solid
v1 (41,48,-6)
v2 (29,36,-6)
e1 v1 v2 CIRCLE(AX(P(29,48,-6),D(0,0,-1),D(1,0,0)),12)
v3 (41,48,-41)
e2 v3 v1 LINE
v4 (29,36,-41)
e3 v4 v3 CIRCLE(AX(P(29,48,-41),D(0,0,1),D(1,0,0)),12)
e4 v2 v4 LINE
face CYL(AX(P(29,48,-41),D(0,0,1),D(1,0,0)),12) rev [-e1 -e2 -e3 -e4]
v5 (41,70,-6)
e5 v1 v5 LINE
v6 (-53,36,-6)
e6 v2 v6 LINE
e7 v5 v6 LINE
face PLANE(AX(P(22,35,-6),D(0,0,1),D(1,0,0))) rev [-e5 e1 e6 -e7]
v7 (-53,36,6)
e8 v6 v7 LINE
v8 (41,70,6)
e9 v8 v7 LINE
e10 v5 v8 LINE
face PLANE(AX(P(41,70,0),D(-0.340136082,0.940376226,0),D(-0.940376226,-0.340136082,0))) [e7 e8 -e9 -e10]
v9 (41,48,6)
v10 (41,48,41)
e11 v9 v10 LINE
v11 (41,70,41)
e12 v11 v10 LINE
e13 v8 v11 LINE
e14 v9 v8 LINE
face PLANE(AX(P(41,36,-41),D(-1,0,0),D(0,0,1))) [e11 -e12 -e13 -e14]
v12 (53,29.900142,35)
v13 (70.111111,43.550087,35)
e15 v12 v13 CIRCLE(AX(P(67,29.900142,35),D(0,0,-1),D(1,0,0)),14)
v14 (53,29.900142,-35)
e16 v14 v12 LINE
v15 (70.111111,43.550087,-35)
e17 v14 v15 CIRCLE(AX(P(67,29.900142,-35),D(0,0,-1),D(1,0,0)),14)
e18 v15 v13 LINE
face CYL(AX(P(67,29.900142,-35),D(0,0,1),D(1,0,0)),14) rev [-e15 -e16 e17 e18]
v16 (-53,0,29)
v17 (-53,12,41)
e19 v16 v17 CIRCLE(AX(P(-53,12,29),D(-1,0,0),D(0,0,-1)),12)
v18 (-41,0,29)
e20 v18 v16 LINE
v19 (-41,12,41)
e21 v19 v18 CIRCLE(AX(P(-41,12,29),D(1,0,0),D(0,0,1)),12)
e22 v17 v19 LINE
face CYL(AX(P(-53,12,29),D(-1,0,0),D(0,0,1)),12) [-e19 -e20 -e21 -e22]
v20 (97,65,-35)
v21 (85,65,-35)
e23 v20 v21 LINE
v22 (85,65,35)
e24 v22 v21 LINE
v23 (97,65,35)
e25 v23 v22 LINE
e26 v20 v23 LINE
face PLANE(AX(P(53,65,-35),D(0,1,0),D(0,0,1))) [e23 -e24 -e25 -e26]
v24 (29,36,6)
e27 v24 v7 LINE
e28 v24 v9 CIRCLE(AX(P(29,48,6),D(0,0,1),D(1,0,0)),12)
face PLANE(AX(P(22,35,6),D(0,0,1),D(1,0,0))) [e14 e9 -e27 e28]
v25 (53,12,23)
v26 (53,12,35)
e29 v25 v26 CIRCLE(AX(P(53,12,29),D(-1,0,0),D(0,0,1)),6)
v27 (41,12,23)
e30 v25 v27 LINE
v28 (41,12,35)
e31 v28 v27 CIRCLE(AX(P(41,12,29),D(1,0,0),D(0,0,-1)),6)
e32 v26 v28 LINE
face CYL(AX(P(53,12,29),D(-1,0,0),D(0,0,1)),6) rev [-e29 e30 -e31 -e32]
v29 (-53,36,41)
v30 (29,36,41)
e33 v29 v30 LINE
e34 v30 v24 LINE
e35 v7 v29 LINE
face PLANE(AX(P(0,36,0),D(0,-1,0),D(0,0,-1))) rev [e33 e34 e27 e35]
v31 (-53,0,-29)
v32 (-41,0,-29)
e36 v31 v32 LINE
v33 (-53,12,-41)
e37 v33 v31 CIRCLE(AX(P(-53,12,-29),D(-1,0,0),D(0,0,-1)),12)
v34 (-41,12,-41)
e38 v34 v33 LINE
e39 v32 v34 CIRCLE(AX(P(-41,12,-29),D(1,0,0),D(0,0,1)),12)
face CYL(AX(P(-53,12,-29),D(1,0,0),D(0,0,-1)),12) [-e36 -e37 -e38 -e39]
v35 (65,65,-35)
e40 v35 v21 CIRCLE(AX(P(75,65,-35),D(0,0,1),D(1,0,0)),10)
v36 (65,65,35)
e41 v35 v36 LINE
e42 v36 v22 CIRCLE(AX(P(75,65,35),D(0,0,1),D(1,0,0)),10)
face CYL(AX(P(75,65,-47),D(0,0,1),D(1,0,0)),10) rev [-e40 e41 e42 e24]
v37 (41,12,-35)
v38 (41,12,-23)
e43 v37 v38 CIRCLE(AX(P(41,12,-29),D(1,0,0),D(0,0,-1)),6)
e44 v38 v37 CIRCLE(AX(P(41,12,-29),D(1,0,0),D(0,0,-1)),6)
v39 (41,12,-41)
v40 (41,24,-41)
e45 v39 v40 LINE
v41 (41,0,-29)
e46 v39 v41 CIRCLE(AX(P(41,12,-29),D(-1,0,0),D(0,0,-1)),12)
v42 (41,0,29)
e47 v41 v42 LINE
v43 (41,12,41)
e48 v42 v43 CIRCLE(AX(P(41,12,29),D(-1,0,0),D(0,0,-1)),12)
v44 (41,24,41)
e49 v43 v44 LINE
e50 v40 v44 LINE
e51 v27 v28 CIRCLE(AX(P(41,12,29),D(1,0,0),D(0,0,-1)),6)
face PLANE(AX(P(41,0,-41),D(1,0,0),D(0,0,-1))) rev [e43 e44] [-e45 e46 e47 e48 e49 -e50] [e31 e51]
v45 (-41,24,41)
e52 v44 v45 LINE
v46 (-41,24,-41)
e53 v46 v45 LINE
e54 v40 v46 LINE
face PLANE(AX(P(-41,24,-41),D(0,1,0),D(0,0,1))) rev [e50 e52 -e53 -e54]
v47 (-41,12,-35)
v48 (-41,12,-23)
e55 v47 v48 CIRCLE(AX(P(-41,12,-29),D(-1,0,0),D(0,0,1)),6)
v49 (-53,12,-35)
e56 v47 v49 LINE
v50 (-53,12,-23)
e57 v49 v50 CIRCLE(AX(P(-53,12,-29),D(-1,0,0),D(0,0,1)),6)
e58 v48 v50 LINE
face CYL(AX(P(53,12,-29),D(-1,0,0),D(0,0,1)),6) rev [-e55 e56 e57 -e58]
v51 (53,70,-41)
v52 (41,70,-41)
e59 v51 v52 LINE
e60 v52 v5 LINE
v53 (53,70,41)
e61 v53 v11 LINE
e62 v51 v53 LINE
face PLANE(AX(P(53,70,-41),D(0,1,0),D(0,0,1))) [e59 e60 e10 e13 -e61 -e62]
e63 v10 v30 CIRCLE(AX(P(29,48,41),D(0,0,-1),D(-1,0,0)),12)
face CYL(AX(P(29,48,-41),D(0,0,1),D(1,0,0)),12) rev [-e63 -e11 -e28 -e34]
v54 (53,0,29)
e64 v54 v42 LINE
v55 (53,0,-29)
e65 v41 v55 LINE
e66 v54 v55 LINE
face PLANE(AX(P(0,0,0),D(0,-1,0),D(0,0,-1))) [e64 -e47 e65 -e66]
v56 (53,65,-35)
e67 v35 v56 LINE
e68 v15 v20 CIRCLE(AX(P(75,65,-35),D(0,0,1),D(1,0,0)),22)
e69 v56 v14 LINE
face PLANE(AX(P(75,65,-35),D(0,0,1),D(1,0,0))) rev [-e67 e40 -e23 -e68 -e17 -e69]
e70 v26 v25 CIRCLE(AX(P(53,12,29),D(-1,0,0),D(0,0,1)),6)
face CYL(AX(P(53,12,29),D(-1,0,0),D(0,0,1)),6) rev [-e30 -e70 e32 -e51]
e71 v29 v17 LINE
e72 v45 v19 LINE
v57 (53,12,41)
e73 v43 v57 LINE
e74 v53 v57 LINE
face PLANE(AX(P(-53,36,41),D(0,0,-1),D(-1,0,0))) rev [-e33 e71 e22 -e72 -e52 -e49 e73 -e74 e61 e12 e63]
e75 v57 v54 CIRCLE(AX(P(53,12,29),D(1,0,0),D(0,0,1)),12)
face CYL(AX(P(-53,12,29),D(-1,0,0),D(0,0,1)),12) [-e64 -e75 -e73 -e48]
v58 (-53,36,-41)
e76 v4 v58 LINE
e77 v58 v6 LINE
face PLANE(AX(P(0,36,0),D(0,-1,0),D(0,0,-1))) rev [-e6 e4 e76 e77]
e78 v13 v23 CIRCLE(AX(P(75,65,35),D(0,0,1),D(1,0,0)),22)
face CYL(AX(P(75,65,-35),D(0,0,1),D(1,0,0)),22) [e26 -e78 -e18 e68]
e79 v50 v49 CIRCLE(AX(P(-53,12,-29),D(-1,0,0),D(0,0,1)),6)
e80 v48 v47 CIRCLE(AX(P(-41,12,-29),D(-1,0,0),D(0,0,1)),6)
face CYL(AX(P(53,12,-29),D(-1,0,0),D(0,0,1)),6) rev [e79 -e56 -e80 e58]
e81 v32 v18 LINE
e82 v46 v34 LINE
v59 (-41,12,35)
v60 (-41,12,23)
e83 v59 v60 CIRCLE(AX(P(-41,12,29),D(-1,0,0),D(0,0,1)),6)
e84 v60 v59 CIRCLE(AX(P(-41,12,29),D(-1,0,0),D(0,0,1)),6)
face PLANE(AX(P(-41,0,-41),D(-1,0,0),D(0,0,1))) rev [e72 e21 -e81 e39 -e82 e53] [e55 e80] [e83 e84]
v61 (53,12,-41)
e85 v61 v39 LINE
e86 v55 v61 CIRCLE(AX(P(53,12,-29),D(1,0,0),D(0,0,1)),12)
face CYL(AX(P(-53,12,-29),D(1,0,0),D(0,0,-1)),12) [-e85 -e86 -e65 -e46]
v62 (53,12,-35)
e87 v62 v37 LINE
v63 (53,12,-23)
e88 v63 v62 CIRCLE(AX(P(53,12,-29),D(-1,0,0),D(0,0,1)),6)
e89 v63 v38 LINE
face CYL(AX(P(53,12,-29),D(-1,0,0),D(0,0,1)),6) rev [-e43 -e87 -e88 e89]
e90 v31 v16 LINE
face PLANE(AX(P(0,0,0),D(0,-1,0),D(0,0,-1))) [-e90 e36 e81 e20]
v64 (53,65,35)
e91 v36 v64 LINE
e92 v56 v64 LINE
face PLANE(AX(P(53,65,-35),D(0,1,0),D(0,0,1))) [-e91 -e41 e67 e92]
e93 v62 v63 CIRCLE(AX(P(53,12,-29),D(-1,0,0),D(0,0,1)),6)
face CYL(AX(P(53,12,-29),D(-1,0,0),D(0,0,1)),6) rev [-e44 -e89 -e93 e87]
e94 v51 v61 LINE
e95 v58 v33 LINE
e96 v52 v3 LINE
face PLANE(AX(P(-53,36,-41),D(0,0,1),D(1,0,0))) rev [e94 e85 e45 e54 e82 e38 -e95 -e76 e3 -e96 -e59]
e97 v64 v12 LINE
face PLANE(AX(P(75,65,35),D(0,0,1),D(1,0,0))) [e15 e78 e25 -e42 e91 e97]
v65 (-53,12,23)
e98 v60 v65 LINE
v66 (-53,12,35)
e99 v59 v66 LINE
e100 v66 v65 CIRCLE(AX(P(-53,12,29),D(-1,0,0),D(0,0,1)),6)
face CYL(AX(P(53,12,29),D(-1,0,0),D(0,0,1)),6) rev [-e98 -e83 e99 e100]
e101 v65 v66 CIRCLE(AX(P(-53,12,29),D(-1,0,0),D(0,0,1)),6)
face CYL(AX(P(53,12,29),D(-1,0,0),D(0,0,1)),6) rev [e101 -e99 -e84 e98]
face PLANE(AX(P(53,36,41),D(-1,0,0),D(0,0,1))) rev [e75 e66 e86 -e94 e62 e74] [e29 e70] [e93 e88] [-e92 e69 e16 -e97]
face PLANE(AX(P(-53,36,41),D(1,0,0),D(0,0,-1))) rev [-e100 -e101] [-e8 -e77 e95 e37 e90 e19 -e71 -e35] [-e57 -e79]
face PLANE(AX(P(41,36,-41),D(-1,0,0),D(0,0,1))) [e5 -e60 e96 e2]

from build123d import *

# Parameters (mm, degrees)
BASE_PROFILE_SKETCH_W         = 106
BASE_PROFILE_SKETCH_H         = 82
BASE_BLOCK_DEPTH              = 36
UNDERSIDE_CHANNEL_SKETCH_W    = 82
UNDERSIDE_CHANNEL_SKETCH_H    = 24
UNDERSIDE_CHANNEL_CUT_DEPTH   = 105.062481231
BASE_CORNER_FILLETS_R12_R     = 12
MOUNTING_HOLES_SKETCH_R       = 6
MOUNTING_HOLES_12_DEPTH       = 120.218287188
UPRIGHT_PLATE_SKETCH_W        = 12
UPRIGHT_PLATE_SKETCH_H        = 34
UPRIGHT_PLATE_DEPTH           = 82
SADDLE_BLOCK_DEPTH            = 70
SADDLE_GROOVE_SKETCH_R        = 10
SADDLE_GROOVE_20_DEPTH        = 82
REINFORCING_RIB_REACH         = 128.452
REINFORCING_RIB_SKETCH_WALL_W = 354.863135512
REINFORCING_RIB_SKETCH_WALL_H = 12
UPRIGHT_PLATE_FILLETS_R12_R   = 12


with BuildPart() as part:
    # Base Profile Sketch → Base Block (new body)
    with BuildSketch(Plane(origin=(0, 0, 0), x_dir=(1, 0, 0), z_dir=(0, 1, 0))):
        Rectangle(BASE_PROFILE_SKETCH_W, BASE_PROFILE_SKETCH_H)
    extrude(amount=BASE_BLOCK_DEPTH)

    # Underside Channel Sketch → Underside Channel Cut (cut, through all)
    with BuildSketch(Plane.XY.offset(41)):
        with Locations((0, 12)):
            Rectangle(UNDERSIDE_CHANNEL_SKETCH_W, UNDERSIDE_CHANNEL_SKETCH_H)
    extrude(amount=-UNDERSIDE_CHANNEL_CUT_DEPTH, mode=Mode.SUBTRACT)

    # Base Corner Fillets R12
    base_corner_fillets_r12_edges = [part.edges().sort_by_distance(p)[0] for p in [
        (47, 0, 41),
        (-47, 0, -41),
        (-47, 0, 41),
        (47, 0, -41),
    ]]
    fillet(base_corner_fillets_r12_edges, radius=BASE_CORNER_FILLETS_R12_R)

    # Mounting Holes Sketch → Mounting Holes Ø12 (cut, through all)
    with BuildSketch(Plane.ZY.offset(53)):
        with Locations((29, 12)):
            Circle(MOUNTING_HOLES_SKETCH_R)
        with Locations((-29, 12)):
            Circle(MOUNTING_HOLES_SKETCH_R)
    extrude(amount=-MOUNTING_HOLES_12_DEPTH, mode=Mode.SUBTRACT)

    # Upright Plate Sketch → Upright Plate (add)
    with BuildSketch(Plane.XY.offset(41)):
        with Locations((47, 53)):
            Rectangle(UPRIGHT_PLATE_SKETCH_W, UPRIGHT_PLATE_SKETCH_H)
    extrude(amount=-UPRIGHT_PLATE_DEPTH)

    # Saddle Block Sketch → Saddle Block (add)
    with BuildSketch(Plane.XY.offset(35)):
        with BuildLine():
            Line((53, 65), (97, 65))
            ThreePointArc((97, 65), (88.719410418, 47.801808881), (70.111111111, 43.550087053))
            ThreePointArc((70.111111111, 43.550087053), (58.269466098, 40.84444589), (53, 29.90014245))
            Line((53, 29.90014245), (53, 65))
        make_face()
    extrude(amount=-SADDLE_BLOCK_DEPTH)

    # Saddle Groove Sketch → Saddle Groove Ø20 (cut)
    with BuildSketch(Plane.XY.offset(35)):
        with Locations((75, 65)):
            Circle(SADDLE_GROOVE_SKETCH_R)
    extrude(amount=-SADDLE_GROOVE_20_DEPTH, mode=Mode.SUBTRACT)

    # Reinforcing Rib Sketch wall → Reinforcing Rib (add, up to next)
    with BuildSketch(Plane(origin=(-6, 53, 0), x_dir=(-0.940376225751, -0.340136081654, 0), z_dir=(0.340136081654, -0.940376225751, 0)), mode=Mode.PRIVATE) as reinforcing_rib_sk1:
        Rectangle(REINFORCING_RIB_SKETCH_WALL_W, REINFORCING_RIB_SKETCH_WALL_H)
    reinforcing_rib_tool1 = extrude(reinforcing_rib_sk1.sketch, amount=REINFORCING_RIB_REACH, mode=Mode.PRIVATE) - part.part
    add(reinforcing_rib_tool1.solids().sort_by_distance((-6, 53, 0))[0])

    # Upright Plate Fillets R12
    upright_plate_fillets_r12_edges = [part.edges().sort_by_distance(p)[0] for p in [
        (41, 36, 23.5),
        (41, 36, -23.5),
    ]]
    fillet(upright_plate_fillets_r12_edges, radius=UPRIGHT_PLATE_FILLETS_R12_R)


solid = part.part
